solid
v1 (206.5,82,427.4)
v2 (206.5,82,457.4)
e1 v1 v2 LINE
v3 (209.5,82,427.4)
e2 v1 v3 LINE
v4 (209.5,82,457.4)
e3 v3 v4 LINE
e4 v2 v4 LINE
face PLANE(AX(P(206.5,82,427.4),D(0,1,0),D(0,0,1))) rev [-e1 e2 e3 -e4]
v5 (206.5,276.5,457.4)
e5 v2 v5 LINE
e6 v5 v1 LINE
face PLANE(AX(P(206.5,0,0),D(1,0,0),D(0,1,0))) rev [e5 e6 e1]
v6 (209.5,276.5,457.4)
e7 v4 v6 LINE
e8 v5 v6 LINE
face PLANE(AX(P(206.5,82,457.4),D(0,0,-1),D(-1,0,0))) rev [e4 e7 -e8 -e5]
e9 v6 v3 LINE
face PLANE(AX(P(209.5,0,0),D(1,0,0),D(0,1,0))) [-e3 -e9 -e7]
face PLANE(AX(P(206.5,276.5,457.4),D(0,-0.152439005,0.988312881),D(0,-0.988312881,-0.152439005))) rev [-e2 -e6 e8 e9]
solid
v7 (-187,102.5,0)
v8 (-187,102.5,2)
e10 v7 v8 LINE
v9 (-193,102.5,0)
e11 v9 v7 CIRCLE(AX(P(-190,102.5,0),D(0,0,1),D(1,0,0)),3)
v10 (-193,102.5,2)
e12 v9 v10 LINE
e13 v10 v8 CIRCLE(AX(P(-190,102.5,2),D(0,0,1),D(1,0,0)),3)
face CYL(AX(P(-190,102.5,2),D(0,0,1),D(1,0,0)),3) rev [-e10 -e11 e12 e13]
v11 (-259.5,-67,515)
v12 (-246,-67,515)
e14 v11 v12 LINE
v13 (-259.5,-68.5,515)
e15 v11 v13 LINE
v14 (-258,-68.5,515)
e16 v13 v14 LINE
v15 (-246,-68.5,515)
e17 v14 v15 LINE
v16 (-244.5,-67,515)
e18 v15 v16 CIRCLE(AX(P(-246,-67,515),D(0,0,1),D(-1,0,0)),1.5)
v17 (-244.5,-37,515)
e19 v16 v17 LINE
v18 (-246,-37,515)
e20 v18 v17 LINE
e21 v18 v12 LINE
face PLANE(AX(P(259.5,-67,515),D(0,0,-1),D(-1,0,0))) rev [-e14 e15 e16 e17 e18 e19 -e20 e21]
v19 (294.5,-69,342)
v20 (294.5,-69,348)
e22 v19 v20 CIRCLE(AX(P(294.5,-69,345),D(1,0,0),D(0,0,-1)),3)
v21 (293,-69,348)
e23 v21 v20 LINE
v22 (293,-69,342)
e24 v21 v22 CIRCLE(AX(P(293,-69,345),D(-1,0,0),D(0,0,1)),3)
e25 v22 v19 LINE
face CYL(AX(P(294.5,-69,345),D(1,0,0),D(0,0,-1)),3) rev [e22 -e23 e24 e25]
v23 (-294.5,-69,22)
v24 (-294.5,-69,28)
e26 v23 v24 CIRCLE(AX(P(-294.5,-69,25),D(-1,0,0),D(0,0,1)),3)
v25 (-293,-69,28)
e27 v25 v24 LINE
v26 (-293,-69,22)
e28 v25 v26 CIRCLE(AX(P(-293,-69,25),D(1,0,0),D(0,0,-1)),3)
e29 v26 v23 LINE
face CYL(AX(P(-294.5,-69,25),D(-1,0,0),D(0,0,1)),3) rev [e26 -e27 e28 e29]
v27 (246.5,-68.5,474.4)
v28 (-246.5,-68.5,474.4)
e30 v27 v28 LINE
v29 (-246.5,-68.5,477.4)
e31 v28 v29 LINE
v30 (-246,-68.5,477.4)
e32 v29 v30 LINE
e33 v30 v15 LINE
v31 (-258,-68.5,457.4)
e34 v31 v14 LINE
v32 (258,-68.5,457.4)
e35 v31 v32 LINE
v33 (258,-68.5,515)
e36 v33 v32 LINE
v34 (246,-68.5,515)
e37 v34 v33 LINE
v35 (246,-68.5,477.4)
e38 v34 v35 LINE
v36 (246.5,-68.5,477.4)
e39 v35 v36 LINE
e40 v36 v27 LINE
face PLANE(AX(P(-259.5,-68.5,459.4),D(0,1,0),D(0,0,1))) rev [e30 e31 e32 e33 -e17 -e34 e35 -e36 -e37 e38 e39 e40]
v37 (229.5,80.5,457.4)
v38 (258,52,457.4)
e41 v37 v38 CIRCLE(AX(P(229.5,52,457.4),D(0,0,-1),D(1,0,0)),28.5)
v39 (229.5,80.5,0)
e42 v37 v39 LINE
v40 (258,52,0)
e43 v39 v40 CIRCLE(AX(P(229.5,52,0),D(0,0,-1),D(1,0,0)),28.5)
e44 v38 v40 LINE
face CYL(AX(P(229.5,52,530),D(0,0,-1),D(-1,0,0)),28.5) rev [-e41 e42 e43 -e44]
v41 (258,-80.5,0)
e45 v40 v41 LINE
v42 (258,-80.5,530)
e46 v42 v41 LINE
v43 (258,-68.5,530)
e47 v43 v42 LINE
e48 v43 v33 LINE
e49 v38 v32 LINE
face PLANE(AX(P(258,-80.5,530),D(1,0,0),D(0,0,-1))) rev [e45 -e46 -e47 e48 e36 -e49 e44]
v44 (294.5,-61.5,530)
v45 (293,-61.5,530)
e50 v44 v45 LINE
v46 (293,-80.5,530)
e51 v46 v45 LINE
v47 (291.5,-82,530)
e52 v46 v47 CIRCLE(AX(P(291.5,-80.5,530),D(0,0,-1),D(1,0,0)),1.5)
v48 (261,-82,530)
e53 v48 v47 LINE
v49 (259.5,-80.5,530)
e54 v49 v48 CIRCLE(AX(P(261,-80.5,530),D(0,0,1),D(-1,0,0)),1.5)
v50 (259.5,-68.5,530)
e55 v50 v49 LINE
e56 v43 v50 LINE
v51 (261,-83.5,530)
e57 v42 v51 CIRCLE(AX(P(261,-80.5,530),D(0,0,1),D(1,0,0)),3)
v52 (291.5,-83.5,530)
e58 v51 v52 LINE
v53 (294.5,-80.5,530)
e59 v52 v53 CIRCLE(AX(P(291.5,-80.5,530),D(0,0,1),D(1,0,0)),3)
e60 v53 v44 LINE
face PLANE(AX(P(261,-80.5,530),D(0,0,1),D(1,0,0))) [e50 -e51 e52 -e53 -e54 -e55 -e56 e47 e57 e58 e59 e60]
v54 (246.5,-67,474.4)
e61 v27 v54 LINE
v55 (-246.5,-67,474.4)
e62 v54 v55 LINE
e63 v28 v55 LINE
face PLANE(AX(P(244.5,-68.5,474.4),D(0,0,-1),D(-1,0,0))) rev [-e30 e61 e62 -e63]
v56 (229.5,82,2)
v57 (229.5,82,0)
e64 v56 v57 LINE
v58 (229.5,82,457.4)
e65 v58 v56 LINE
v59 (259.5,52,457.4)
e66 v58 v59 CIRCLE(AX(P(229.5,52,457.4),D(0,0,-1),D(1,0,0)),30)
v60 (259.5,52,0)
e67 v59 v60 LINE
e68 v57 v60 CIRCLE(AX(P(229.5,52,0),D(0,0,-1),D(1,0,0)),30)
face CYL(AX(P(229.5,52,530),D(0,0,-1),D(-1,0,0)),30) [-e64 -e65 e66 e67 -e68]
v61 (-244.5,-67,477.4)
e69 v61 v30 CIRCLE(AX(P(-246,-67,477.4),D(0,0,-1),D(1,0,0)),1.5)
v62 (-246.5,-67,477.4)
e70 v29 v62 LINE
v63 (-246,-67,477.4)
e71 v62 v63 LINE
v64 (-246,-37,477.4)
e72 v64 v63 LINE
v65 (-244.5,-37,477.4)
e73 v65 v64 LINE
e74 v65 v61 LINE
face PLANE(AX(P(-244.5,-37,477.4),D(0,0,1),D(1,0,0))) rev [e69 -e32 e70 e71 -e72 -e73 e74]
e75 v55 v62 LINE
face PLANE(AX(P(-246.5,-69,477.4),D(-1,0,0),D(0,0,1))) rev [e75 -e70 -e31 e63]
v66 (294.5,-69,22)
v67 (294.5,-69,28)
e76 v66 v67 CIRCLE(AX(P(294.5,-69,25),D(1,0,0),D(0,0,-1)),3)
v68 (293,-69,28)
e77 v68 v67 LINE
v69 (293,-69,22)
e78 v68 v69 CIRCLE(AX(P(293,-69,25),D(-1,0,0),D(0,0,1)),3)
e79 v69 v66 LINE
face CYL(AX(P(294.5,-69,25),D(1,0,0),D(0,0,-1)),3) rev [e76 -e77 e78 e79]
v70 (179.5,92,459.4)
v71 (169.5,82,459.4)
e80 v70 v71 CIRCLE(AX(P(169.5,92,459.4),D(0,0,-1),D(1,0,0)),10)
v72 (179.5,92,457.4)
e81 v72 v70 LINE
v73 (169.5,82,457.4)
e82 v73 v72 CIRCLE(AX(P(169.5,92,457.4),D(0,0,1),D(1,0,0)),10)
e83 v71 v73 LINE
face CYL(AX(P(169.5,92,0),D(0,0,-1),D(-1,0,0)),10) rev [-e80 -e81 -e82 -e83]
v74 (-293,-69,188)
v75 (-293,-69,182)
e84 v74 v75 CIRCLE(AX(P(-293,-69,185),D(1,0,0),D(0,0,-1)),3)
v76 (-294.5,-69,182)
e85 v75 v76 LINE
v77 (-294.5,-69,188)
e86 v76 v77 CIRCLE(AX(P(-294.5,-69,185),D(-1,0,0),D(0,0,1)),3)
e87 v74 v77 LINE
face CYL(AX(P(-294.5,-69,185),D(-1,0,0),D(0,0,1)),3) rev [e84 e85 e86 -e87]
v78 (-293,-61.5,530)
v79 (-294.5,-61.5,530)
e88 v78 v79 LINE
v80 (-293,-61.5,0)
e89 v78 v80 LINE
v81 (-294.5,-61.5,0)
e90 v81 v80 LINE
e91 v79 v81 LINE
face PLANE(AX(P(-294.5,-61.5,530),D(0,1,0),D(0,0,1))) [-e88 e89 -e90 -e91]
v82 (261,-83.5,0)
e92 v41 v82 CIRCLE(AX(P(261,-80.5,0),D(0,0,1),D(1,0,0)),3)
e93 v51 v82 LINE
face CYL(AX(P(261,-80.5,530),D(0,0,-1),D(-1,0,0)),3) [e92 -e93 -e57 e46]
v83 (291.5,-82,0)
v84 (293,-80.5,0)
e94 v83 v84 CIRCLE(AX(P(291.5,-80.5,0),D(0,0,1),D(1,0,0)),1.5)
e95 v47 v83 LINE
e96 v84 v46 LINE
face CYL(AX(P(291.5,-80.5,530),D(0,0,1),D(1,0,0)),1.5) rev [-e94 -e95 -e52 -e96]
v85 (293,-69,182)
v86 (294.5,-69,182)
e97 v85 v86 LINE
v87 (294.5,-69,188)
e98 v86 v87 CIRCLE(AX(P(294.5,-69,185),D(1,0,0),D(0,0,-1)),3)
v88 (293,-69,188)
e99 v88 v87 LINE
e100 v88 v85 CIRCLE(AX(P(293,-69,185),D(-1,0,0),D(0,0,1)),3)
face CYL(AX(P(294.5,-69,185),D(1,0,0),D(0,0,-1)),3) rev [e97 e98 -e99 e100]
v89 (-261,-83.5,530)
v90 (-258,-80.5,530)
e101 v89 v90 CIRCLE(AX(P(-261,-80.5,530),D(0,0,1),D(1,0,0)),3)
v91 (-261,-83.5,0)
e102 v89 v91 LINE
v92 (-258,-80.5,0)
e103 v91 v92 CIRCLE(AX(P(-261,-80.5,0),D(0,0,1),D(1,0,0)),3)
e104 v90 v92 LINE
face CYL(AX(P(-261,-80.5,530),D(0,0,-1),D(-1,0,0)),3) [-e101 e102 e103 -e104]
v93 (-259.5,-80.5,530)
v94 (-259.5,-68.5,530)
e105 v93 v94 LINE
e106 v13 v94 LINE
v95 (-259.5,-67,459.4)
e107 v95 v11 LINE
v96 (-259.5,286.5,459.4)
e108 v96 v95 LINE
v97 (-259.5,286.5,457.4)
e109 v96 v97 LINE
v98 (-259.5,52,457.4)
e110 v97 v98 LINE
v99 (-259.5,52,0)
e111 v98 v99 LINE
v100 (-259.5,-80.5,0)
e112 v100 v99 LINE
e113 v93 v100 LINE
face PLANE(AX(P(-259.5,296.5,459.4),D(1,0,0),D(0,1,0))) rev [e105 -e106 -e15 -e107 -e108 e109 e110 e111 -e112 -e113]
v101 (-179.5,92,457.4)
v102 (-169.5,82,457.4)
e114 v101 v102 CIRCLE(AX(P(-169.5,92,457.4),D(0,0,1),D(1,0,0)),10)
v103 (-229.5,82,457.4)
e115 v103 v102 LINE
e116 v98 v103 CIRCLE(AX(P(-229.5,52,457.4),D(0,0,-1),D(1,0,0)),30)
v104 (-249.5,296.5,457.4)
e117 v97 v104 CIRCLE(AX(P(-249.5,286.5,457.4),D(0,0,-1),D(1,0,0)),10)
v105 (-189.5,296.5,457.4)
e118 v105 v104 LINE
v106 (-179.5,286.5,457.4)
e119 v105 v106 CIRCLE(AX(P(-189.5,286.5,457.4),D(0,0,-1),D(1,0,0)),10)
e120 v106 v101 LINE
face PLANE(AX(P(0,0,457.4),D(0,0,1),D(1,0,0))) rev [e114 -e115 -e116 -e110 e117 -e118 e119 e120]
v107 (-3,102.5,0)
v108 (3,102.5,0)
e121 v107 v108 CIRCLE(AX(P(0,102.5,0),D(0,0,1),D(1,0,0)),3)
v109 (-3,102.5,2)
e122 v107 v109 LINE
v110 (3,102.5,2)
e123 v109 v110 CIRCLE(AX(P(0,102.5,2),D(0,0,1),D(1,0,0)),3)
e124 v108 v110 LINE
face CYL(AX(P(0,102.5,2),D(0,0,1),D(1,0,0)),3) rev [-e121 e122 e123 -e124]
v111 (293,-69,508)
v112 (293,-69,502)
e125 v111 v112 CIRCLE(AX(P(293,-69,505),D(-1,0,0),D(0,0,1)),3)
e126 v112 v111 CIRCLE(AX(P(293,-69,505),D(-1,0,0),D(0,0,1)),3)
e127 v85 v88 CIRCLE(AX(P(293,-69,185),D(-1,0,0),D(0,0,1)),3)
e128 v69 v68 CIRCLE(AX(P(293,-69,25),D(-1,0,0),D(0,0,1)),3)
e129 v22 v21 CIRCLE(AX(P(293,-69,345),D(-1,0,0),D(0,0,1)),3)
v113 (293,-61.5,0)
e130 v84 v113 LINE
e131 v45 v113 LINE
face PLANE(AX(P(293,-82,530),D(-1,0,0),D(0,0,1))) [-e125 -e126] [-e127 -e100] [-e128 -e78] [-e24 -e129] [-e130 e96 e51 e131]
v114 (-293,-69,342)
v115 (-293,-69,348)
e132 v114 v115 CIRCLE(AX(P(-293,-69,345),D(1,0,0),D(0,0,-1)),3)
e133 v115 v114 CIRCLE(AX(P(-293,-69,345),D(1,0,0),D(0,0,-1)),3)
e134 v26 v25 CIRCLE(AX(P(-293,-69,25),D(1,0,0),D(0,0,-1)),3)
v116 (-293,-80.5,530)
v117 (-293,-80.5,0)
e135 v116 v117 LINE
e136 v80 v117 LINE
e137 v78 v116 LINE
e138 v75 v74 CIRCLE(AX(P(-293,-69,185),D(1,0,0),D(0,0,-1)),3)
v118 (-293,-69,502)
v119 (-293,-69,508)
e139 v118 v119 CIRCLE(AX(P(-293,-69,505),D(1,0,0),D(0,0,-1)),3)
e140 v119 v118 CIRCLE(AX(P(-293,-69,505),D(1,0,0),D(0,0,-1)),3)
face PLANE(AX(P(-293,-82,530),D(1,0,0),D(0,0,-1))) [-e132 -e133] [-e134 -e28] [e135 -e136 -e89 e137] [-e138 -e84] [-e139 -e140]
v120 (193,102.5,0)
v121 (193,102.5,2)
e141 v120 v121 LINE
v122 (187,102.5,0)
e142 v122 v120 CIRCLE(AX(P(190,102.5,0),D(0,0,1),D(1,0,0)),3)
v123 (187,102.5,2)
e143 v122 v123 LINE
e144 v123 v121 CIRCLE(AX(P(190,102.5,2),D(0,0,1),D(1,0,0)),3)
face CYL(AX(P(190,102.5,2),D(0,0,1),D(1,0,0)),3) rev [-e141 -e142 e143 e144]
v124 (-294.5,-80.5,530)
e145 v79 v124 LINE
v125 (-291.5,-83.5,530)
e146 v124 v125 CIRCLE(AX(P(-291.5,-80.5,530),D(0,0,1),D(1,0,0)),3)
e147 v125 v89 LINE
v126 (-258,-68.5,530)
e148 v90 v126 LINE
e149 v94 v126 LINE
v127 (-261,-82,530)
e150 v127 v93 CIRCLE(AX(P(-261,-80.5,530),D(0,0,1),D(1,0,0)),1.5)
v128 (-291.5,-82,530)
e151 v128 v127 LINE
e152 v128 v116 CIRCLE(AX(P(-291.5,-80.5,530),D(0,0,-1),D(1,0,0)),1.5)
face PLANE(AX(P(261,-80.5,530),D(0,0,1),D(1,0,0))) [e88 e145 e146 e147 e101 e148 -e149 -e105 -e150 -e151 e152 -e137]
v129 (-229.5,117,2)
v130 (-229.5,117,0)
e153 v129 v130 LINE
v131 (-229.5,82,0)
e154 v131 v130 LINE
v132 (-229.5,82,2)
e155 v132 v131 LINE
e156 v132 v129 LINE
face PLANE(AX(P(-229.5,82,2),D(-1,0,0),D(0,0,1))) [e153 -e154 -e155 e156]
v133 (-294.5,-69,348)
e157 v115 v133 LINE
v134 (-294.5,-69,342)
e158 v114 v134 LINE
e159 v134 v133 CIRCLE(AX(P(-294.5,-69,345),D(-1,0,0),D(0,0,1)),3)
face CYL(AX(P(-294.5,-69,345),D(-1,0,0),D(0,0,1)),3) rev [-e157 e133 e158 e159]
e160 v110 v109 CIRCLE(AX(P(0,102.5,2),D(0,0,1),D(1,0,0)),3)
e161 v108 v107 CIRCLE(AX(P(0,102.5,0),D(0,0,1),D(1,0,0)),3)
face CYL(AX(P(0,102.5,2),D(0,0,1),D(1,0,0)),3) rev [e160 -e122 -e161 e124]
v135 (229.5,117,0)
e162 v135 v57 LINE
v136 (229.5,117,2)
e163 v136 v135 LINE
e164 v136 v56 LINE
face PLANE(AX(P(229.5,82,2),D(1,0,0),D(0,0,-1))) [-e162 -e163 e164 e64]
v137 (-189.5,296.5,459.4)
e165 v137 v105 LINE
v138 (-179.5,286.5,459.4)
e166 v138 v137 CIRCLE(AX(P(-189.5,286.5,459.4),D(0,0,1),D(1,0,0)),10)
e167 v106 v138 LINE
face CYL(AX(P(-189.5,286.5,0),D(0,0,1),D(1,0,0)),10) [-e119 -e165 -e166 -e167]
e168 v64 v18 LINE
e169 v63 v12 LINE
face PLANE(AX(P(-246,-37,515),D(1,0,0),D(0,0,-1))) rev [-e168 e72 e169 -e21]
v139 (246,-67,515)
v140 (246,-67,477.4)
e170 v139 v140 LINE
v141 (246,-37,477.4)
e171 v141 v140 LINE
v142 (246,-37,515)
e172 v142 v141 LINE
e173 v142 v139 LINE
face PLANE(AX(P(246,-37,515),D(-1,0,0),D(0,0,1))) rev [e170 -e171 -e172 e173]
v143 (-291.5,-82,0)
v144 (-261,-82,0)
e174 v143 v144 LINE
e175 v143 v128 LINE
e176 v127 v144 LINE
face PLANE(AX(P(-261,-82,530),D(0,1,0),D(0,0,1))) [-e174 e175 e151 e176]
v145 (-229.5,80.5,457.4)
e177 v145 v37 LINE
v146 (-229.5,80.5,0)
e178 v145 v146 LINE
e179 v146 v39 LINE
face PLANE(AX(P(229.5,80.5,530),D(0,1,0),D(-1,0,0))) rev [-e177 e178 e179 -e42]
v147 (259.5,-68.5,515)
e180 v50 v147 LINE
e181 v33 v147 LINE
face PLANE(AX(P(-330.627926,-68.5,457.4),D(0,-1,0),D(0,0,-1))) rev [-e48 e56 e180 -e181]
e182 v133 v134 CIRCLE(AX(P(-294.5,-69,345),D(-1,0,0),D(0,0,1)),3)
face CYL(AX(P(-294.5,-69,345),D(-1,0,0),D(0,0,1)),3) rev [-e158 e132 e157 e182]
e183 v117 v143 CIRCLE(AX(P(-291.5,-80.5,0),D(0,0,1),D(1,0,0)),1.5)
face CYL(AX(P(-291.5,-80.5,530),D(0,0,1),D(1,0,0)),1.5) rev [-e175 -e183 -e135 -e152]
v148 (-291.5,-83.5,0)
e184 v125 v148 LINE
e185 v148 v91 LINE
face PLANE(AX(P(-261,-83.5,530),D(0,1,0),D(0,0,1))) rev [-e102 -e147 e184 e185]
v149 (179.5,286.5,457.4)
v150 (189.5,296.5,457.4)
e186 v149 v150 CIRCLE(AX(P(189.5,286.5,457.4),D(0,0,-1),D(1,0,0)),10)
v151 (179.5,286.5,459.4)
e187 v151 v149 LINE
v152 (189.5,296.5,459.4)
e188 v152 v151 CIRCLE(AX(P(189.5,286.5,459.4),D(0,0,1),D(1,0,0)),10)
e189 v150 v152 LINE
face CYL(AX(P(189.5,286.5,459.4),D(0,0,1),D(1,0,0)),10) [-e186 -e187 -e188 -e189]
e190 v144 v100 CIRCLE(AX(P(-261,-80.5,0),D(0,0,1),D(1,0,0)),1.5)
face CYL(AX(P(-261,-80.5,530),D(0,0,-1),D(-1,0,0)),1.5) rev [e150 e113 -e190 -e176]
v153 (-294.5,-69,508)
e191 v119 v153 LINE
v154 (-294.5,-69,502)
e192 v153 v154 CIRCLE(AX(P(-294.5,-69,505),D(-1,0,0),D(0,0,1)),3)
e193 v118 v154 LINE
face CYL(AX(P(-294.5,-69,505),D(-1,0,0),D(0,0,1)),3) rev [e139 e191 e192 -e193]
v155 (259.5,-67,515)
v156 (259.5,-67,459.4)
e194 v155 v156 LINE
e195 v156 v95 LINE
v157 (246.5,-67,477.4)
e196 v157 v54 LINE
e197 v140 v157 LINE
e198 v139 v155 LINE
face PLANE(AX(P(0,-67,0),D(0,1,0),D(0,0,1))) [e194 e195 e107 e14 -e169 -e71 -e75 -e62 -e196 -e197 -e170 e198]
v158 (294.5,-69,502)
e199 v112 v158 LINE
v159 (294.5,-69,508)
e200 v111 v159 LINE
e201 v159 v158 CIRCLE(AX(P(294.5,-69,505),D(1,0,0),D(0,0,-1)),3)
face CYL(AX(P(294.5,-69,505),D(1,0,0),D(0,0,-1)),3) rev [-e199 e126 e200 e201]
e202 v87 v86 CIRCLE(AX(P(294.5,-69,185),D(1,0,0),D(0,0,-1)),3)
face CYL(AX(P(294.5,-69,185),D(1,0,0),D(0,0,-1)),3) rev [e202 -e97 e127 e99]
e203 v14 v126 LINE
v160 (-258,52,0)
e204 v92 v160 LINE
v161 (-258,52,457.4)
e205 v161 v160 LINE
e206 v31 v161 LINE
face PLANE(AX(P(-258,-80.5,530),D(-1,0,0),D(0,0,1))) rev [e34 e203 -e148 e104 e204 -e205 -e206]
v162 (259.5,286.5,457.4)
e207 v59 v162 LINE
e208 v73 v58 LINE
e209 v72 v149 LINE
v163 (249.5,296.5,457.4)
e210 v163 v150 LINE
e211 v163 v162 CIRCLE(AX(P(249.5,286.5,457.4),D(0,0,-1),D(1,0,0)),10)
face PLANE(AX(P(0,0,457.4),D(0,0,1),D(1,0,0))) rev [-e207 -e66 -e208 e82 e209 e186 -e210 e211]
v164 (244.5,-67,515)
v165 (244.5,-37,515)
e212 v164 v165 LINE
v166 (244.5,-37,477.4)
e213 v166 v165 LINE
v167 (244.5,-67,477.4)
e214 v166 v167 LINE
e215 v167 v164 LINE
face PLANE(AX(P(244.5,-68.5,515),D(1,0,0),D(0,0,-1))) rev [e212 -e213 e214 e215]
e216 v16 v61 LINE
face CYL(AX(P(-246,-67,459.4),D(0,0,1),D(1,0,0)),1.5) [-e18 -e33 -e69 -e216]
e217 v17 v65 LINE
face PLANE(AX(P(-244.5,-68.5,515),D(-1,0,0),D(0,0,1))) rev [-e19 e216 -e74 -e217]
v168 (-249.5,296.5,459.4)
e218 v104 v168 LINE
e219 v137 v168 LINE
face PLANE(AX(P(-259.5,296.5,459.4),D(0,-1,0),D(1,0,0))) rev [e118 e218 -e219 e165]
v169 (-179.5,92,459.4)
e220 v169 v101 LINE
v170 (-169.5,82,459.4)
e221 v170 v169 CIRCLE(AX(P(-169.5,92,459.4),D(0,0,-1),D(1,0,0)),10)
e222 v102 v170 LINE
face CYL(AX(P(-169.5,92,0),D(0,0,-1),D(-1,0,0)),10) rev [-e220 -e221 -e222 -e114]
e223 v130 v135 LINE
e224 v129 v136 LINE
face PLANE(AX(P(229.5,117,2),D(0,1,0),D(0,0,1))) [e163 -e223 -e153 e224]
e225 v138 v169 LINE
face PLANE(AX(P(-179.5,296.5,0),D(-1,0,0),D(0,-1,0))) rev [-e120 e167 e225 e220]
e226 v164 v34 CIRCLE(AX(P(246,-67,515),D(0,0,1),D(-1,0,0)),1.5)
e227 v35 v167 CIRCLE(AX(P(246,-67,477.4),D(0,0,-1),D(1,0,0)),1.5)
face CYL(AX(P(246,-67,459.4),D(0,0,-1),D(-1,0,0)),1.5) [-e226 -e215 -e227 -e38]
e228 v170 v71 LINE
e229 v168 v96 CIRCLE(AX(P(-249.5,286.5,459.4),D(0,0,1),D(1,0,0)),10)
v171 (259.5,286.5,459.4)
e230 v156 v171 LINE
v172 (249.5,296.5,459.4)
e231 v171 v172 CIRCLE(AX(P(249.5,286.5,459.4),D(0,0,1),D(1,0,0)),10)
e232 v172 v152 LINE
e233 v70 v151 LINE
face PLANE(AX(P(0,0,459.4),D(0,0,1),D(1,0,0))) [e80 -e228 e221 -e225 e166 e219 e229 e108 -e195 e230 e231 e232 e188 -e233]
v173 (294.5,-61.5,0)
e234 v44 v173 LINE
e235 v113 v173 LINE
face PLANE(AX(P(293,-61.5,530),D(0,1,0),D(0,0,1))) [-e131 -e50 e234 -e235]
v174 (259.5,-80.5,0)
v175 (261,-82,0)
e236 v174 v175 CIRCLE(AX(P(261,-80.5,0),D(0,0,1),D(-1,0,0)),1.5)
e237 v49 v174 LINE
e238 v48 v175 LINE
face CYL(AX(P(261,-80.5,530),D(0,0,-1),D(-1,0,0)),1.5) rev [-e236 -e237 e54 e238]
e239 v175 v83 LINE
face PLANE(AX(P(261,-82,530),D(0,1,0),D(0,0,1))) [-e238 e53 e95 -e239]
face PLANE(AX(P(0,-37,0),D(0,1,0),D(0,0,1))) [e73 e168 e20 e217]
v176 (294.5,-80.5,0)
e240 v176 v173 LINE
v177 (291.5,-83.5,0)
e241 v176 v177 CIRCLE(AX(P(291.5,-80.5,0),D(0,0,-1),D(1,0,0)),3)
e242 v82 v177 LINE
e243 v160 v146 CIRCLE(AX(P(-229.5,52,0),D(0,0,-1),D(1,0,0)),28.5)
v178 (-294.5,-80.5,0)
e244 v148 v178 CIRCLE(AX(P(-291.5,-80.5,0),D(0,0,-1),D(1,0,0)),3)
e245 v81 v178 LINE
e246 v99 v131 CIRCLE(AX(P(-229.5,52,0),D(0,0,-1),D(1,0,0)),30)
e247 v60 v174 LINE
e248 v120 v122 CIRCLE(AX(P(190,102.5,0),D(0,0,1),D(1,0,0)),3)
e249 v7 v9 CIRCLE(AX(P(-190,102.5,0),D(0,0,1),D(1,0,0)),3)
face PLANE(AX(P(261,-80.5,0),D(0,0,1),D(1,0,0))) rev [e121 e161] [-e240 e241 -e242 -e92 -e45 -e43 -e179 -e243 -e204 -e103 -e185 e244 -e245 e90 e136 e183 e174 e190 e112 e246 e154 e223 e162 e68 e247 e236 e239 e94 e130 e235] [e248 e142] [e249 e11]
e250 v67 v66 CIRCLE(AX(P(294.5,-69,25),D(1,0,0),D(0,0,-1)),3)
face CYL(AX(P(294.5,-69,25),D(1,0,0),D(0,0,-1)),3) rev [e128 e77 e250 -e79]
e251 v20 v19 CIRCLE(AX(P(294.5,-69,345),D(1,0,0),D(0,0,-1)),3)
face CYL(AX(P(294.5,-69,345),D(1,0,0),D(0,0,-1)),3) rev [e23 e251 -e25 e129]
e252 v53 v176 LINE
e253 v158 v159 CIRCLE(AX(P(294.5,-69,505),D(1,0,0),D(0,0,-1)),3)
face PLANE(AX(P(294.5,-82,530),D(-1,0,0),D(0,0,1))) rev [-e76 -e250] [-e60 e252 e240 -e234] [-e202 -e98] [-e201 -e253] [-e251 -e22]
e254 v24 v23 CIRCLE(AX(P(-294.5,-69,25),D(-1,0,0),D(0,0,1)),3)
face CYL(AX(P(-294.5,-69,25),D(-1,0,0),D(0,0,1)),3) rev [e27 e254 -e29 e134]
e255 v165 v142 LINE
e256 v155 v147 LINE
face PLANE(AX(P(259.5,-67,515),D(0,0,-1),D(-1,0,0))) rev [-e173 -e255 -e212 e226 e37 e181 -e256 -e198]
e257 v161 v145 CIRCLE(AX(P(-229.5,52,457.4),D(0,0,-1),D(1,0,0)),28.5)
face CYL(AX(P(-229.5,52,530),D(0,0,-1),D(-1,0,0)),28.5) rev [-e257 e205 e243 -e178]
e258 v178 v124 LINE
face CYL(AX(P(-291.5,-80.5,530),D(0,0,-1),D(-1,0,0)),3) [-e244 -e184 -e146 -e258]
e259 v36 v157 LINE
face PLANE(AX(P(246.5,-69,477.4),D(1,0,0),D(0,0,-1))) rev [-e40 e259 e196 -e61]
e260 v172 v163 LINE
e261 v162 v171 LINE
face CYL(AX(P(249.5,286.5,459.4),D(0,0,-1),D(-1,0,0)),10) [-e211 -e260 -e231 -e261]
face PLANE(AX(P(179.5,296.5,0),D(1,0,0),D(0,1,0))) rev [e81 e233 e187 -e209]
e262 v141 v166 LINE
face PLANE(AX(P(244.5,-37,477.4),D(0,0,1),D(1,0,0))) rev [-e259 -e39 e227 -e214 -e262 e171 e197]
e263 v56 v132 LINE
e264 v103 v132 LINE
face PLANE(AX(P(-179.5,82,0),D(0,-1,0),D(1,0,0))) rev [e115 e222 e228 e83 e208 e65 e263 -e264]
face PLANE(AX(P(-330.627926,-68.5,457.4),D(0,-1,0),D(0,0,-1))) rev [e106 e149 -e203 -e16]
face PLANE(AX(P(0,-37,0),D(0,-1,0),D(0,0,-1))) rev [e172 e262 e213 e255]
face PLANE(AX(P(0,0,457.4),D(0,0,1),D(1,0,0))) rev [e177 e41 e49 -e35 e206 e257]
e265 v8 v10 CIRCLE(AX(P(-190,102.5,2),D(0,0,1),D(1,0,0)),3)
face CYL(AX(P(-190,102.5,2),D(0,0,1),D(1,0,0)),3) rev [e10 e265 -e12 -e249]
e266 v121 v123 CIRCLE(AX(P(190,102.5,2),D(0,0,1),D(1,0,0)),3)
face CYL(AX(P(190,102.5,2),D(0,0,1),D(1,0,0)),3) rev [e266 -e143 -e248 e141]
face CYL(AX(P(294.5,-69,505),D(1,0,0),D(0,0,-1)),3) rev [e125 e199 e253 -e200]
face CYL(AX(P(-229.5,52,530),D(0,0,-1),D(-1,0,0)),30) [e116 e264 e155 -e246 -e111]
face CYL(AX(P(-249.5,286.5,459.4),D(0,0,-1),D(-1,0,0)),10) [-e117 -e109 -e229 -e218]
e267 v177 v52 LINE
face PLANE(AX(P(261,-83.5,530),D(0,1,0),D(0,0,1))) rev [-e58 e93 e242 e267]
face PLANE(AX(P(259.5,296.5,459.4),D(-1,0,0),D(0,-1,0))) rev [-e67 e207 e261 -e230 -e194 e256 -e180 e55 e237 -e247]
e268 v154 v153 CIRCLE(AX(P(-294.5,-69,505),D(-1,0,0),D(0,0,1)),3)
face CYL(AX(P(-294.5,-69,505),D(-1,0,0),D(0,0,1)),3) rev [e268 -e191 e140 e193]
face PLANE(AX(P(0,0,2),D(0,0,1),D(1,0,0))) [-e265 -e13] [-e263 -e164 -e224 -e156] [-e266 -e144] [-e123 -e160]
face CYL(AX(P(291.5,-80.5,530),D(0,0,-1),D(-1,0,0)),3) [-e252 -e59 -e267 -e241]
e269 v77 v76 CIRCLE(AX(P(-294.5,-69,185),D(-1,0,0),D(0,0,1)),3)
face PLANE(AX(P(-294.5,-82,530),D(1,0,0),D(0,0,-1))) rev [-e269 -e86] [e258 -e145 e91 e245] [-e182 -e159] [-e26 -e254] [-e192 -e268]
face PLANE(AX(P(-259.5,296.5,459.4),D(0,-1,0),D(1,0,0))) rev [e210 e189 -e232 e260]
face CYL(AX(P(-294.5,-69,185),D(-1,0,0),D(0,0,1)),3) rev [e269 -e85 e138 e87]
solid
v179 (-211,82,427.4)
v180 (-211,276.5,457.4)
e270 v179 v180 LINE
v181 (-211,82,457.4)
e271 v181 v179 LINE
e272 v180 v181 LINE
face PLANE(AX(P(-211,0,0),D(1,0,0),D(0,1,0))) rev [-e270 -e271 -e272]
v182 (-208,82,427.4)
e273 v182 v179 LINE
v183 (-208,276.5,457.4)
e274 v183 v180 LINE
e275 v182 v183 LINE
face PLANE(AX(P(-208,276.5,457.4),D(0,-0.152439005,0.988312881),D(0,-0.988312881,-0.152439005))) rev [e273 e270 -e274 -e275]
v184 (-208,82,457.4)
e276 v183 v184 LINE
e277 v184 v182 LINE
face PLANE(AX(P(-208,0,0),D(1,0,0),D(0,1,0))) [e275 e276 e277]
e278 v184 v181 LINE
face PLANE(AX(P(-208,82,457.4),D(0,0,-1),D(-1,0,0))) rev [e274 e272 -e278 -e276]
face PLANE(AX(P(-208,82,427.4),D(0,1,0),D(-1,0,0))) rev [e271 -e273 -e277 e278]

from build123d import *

# Parameters (mm, degrees)
EXTRUDE_1_DEPTH                = 530
FILLET_1_R                     = 3
FILLET_6_R                     = 1.5
SKETCH_2_W                     = 651.298886305
SKETCH_2_H                     = 207.751760279
CUT_EXTRUDE_1_DEPTH            = 72.6
SKETCH_4_W                     = 519
SKETCH_4_H                     = 365
EXTRUDE_10_DEPTH               = 2
SKETCH_5_W                     = 359
SKETCH_5_H                     = 214.5
CUT_EXTRUDE_2_DEPTH            = 622.04014363
FILLET_2_R                     = 10
FILLET_3_R                     = 10
EXTRUDE_13_DEPTH               = 1.5
EXTRUDE_14_DEPTH               = 3
FILLET_4_R                     = 10
SKETCH_13_W                    = 519
SKETCH_13_H                    = 55.6
EXTRUDE_15_DEPTH               = 1.5
SKETCH_14_W                    = 489
SKETCH_14_H                    = 40.6
CUT_EXTRUDE_5_DEPTH            = 1.5
SKETCH_15_W                    = 1.5
SKETCH_15_H                    = 37.6
EXTRUDE_16_DEPTH               = 30
SKETCH_16_W                    = 2
SKETCH_16_H                    = 3
CUT_EXTRUDE_6_DEPTH            = 2
FILLET_5_R                     = 1.5
SKETCH_17_W                    = 459
SKETCH_17_H                    = 35
EXTRUDE_17_DEPTH               = 2
SKETCH_18_W                    = 3
SKETCH_18_H                    = 2
HOLE_WIZARD_6_0_6_1_AT_2_COUNT = 2
HOLE_WIZARD_6_0_6_1_AT_2_PITCH = 190
HOLE_WIZARD_6_0_6_1_AT_3_COUNT = 2
HOLE_WIZARD_6_0_6_1_AT_3_PITCH = 380
SKETCH_20_W                    = 1.5
SKETCH_20_H                    = 7
EXTRUDE_18_DEPTH               = 72.6
HOLE_WIZARD_6_0_6_2_AT_2_COUNT = 2
HOLE_WIZARD_6_0_6_2_AT_2_PITCH = 160
HOLE_WIZARD_6_0_6_2_AT_3_COUNT = 2
HOLE_WIZARD_6_0_6_2_AT_3_PITCH = 320
HOLE_WIZARD_6_0_6_2_AT_4_COUNT = 2
HOLE_WIZARD_6_0_6_2_AT_4_PITCH = 480
HOLE_WIZARD_6_0_6_3_AT_2_COUNT = 2
HOLE_WIZARD_6_0_6_3_AT_2_PITCH = 160
HOLE_WIZARD_6_0_6_3_AT_3_COUNT = 2
HOLE_WIZARD_6_0_6_3_AT_3_PITCH = 320
HOLE_WIZARD_6_0_6_3_AT_4_COUNT = 2
HOLE_WIZARD_6_0_6_3_AT_4_PITCH = 480


with BuildPart() as part:
    # 草图1 → 拉伸-薄壁1 (new body)
    with BuildSketch(Plane.XY):
        with BuildLine():
            Line((293, -61.5), (293, -82))
            Line((293, -82), (261, -82))
            ThreePointArc((261, -82), (259.939339828, -81.560660172), (259.5, -80.5))
            Line((259.5, -80.5), (259.5, 52))
            ThreePointArc((259.5, 52), (250.713203436, 73.213203436), (229.5, 82))
            Line((229.5, 82), (-229.5, 82))
            ThreePointArc((-229.5, 82), (-250.713203436, 73.213203436), (-259.5, 52))
            Line((-259.5, 52), (-259.5, -80.5))
            ThreePointArc((-259.5, -80.5), (-259.939339828, -81.560660172), (-261, -82))
            Line((-261, -82), (-293, -82))
            Line((-293, -82), (-293, -61.5))
            Line((-293, -61.5), (-294.5, -61.5))
            Line((-294.5, -61.5), (-294.5, -83.5))
            Line((-294.5, -83.5), (-261, -83.5))
            ThreePointArc((-261, -83.5), (-258.878679656, -82.621320344), (-258, -80.5))
            Line((-258, -80.5), (-258, 52))
            ThreePointArc((-258, 52), (-249.652543264, 72.152543264), (-229.5, 80.5))
            Line((-229.5, 80.5), (229.5, 80.5))
            ThreePointArc((229.5, 80.5), (249.652543264, 72.152543264), (258, 52))
            Line((258, 52), (258, -80.5))
            ThreePointArc((258, -80.5), (258.878679656, -82.621320344), (261, -83.5))
            Line((261, -83.5), (294.5, -83.5))
            Line((294.5, -83.5), (294.5, -61.5))
            Line((294.5, -61.5), (293, -61.5))
        make_face()
    extrude(amount=EXTRUDE_1_DEPTH)

    # 圆角1
    fillet_1_edges = [part.edges().sort_by_distance(p)[0] for p in [
        (294.5, -83.5, 265),
        (-294.5, -83.5, 265),
    ]]
    fillet(fillet_1_edges, radius=FILLET_1_R)

    # 圆角6
    fillet_6_edges = [part.edges().sort_by_distance(p)[0] for p in [
        (-293, -82, 265),
        (293, -82, 265),
    ]]
    fillet(fillet_6_edges, radius=FILLET_6_R)

    # 草图2 → 切除-拉伸1 (cut)
    with BuildSketch(Plane.XY.offset(530)):
        with Locations((-4.978482744, 35.375880139)):
            Rectangle(SKETCH_2_W, SKETCH_2_H)
    extrude(amount=-CUT_EXTRUDE_1_DEPTH, mode=Mode.SUBTRACT)



with BuildPart() as body_2:
    # 草图4 → 凸台-拉伸10 (new body)
    with BuildSketch(Plane.XY.offset(457.4)):
        with Locations((0, 114)):
            Rectangle(SKETCH_4_W, SKETCH_4_H)
    extrude(amount=EXTRUDE_10_DEPTH)

    # 草图5 → 切除-拉伸2 (cut, through all)
    with BuildSketch(Plane.XY.offset(459.4)):
        with Locations((0, 189.25)):
            Rectangle(SKETCH_5_W, SKETCH_5_H)
    extrude(amount=-CUT_EXTRUDE_2_DEPTH, mode=Mode.SUBTRACT)

    # 圆角2
    fillet_2_edges = [body_2.edges().sort_by_distance(p)[0] for p in [
        (179.5, 82, 458.4),
    ]]
    fillet(fillet_2_edges, radius=FILLET_2_R)

    # 圆角3
    fillet_3_edges = [body_2.edges().sort_by_distance(p)[0] for p in [
        (-179.5, 82, 458.4),
    ]]
    fillet(fillet_3_edges, radius=FILLET_3_R)

    # 圆角4
    fillet_4_edges = [body_2.edges().sort_by_distance(p)[0] for p in [
        (-179.5, 296.5, 458.4),
        (179.5, 296.5, 458.4),
        (-259.5, 296.5, 458.4),
        (259.5, 296.5, 458.4),
    ]]
    fillet(fillet_4_edges, radius=FILLET_4_R)


with BuildPart() as body_3:
    # 草图6 → 凸台-拉伸13 (new, symmetric)
    with BuildSketch(Plane(origin=(-209.5, 0, 0), x_dir=(0, 0, -1), z_dir=(1, 0, 0))):
        Polygon((-457.4, 276.5), (-427.4, 82), (-457.4, 82), align=None)
    extrude(amount=EXTRUDE_13_DEPTH, both=True)


with BuildPart() as body_4:
    # 草图8 → 凸台-拉伸14 (new body)
    with BuildSketch(Plane.ZY.offset(-209.5)):
        Polygon((457.4, 276.5), (427.4, 82), (457.4, 82), align=None)
    extrude(amount=EXTRUDE_14_DEPTH)


with BuildPart() as part_1:
    add(part.part)

    add(body_2.part)  # 凸台-拉伸15 merges body 2
    # 草图13 → 凸台-拉伸15 (add)
    with BuildSketch(Plane(origin=(0, -68.5, 0), x_dir=(1, 0, 0), z_dir=(0, 1, 0))):
        with Locations((0, -487.2)):
            Rectangle(SKETCH_13_W, SKETCH_13_H)
    extrude(amount=EXTRUDE_15_DEPTH)

    # 草图14 → 切除-拉伸5 (cut)
    with BuildSketch(Plane(origin=(0, -67, 0), x_dir=(1, 0, 0), z_dir=(0, 1, 0))):
        with Locations((0, -494.7)):
            Rectangle(SKETCH_14_W, SKETCH_14_H)
    extrude(amount=-CUT_EXTRUDE_5_DEPTH, mode=Mode.SUBTRACT)

    # 草图15 → 凸台-拉伸16 (add)
    with BuildSketch(Plane(origin=(0, -67, 0), x_dir=(1, 0, 0), z_dir=(0, 1, 0))):
        with Locations((245.25, -496.2)):
            Rectangle(SKETCH_15_W, SKETCH_15_H)
        with Locations((-245.25, -496.2)):
            Rectangle(SKETCH_15_W, SKETCH_15_H)
    extrude(amount=EXTRUDE_16_DEPTH)

    # 草图16 → 切除-拉伸6 (cut)
    with BuildSketch(Plane(origin=(0, -67, 0), x_dir=(1, 0, 0), z_dir=(0, 1, 0))):
        with Locations((245.5, -475.9)):
            Rectangle(SKETCH_16_W, SKETCH_16_H)
        with Locations((-245.5, -475.9)):
            Rectangle(SKETCH_16_W, SKETCH_16_H)
    extrude(amount=-CUT_EXTRUDE_6_DEPTH, mode=Mode.SUBTRACT)

    # 圆角5
    fillet_5_edges = [part_1.edges().sort_by_distance(p)[0] for p in [
        (244.5, -68.5, 496.2),
        (-244.5, -68.5, 496.2),
    ]]
    fillet(fillet_5_edges, radius=FILLET_5_R)

    # 草图17 → 凸台-拉伸17 (add)
    with BuildSketch(Plane(origin=(0, 0, 0), x_dir=(-1, 0, 0), z_dir=(0, 0, -1))):
        with Locations((0, 99.5)):
            Rectangle(SKETCH_17_W, SKETCH_17_H)
    extrude(amount=-EXTRUDE_17_DEPTH)

    # 草图18 → Ø6.0 (6) 直径孔1 (revolve, cut)
    with BuildSketch(Plane(origin=(-190, 102.5, 2), x_dir=(0, -1, 0), z_dir=(1, 0, 0))):
        with Locations((1.5, 1)):
            Rectangle(SKETCH_18_W, SKETCH_18_H)
    hole_wizard_6_0_6_1 = revolve(axis=Axis((-190, 102.5, 8.35), (0, 0, -1)), mode=Mode.SUBTRACT)

    # Ø6.0 (6) 直径孔1 at 2: Ø6.0 (6) 直径孔1 ×2
    with Locations(*[(i * HOLE_WIZARD_6_0_6_1_AT_2_PITCH, 0, 0) for i in range(1, HOLE_WIZARD_6_0_6_1_AT_2_COUNT)]):
        add(hole_wizard_6_0_6_1, mode=Mode.SUBTRACT)

    # Ø6.0 (6) 直径孔1 at 3: Ø6.0 (6) 直径孔1 ×2
    with Locations(*[(i * HOLE_WIZARD_6_0_6_1_AT_3_PITCH, 0, 0) for i in range(1, HOLE_WIZARD_6_0_6_1_AT_3_COUNT)]):
        add(hole_wizard_6_0_6_1, mode=Mode.SUBTRACT)

    # 草图20 → 凸台-拉伸18 (add)
    with BuildSketch(Plane.XY.offset(457.4)):
        with Locations((293.75, -65)):
            Rectangle(SKETCH_20_W, SKETCH_20_H)
        with Locations((-293.75, -65)):
            Rectangle(SKETCH_20_W, SKETCH_20_H)
    extrude(amount=EXTRUDE_18_DEPTH)

    # 草图21 → Ø6.0 (6) 直径孔2 (revolve, cut)
    with BuildSketch(Plane(origin=(294.5, -69, 505), x_dir=(0, 0, -1), z_dir=(0, 1, 0))):
        Polygon((0, 0), (0, 3.802581857), (3, 2), (3, 0), align=None)
    hole_wizard_6_0_6_2 = revolve(axis=Axis((300.85, -69, 505), (-1, 0, 0)), mode=Mode.SUBTRACT)

    # Ø6.0 (6) 直径孔2 at 2: Ø6.0 (6) 直径孔2 ×2
    with Locations(*[(0, 0, -i * HOLE_WIZARD_6_0_6_2_AT_2_PITCH) for i in range(1, HOLE_WIZARD_6_0_6_2_AT_2_COUNT)]):
        add(hole_wizard_6_0_6_2, mode=Mode.SUBTRACT)

    # Ø6.0 (6) 直径孔2 at 3: Ø6.0 (6) 直径孔2 ×2
    with Locations(*[(0, 0, -i * HOLE_WIZARD_6_0_6_2_AT_3_PITCH) for i in range(1, HOLE_WIZARD_6_0_6_2_AT_3_COUNT)]):
        add(hole_wizard_6_0_6_2, mode=Mode.SUBTRACT)

    # Ø6.0 (6) 直径孔2 at 4: Ø6.0 (6) 直径孔2 ×2
    with Locations(*[(0, 0, -i * HOLE_WIZARD_6_0_6_2_AT_4_PITCH) for i in range(1, HOLE_WIZARD_6_0_6_2_AT_4_COUNT)]):
        add(hole_wizard_6_0_6_2, mode=Mode.SUBTRACT)

    # 草图23 → Ø6.0 (6) 直径孔3 (revolve, cut)
    with BuildSketch(Plane(origin=(-294.5, -69, 25), x_dir=(0, 0, 1), z_dir=(0, 1, 0))):
        Polygon((0, 0), (0, 3.802581857), (3, 2), (3, 0), align=None)
    hole_wizard_6_0_6_3 = revolve(axis=Axis((-300.85, -69, 25), (1, 0, 0)), mode=Mode.SUBTRACT)

    # Ø6.0 (6) 直径孔3 at 2: Ø6.0 (6) 直径孔3 ×2
    with Locations(*[(0, 0, i * HOLE_WIZARD_6_0_6_3_AT_2_PITCH) for i in range(1, HOLE_WIZARD_6_0_6_3_AT_2_COUNT)]):
        add(hole_wizard_6_0_6_3, mode=Mode.SUBTRACT)

    # Ø6.0 (6) 直径孔3 at 3: Ø6.0 (6) 直径孔3 ×2
    with Locations(*[(0, 0, i * HOLE_WIZARD_6_0_6_3_AT_3_PITCH) for i in range(1, HOLE_WIZARD_6_0_6_3_AT_3_COUNT)]):
        add(hole_wizard_6_0_6_3, mode=Mode.SUBTRACT)

    # Ø6.0 (6) 直径孔3 at 4: Ø6.0 (6) 直径孔3 ×2
    with Locations(*[(0, 0, i * HOLE_WIZARD_6_0_6_3_AT_4_PITCH) for i in range(1, HOLE_WIZARD_6_0_6_3_AT_4_COUNT)]):
        add(hole_wizard_6_0_6_3, mode=Mode.SUBTRACT)


solid = Compound([body_3.part, body_4.part, part_1.part])
